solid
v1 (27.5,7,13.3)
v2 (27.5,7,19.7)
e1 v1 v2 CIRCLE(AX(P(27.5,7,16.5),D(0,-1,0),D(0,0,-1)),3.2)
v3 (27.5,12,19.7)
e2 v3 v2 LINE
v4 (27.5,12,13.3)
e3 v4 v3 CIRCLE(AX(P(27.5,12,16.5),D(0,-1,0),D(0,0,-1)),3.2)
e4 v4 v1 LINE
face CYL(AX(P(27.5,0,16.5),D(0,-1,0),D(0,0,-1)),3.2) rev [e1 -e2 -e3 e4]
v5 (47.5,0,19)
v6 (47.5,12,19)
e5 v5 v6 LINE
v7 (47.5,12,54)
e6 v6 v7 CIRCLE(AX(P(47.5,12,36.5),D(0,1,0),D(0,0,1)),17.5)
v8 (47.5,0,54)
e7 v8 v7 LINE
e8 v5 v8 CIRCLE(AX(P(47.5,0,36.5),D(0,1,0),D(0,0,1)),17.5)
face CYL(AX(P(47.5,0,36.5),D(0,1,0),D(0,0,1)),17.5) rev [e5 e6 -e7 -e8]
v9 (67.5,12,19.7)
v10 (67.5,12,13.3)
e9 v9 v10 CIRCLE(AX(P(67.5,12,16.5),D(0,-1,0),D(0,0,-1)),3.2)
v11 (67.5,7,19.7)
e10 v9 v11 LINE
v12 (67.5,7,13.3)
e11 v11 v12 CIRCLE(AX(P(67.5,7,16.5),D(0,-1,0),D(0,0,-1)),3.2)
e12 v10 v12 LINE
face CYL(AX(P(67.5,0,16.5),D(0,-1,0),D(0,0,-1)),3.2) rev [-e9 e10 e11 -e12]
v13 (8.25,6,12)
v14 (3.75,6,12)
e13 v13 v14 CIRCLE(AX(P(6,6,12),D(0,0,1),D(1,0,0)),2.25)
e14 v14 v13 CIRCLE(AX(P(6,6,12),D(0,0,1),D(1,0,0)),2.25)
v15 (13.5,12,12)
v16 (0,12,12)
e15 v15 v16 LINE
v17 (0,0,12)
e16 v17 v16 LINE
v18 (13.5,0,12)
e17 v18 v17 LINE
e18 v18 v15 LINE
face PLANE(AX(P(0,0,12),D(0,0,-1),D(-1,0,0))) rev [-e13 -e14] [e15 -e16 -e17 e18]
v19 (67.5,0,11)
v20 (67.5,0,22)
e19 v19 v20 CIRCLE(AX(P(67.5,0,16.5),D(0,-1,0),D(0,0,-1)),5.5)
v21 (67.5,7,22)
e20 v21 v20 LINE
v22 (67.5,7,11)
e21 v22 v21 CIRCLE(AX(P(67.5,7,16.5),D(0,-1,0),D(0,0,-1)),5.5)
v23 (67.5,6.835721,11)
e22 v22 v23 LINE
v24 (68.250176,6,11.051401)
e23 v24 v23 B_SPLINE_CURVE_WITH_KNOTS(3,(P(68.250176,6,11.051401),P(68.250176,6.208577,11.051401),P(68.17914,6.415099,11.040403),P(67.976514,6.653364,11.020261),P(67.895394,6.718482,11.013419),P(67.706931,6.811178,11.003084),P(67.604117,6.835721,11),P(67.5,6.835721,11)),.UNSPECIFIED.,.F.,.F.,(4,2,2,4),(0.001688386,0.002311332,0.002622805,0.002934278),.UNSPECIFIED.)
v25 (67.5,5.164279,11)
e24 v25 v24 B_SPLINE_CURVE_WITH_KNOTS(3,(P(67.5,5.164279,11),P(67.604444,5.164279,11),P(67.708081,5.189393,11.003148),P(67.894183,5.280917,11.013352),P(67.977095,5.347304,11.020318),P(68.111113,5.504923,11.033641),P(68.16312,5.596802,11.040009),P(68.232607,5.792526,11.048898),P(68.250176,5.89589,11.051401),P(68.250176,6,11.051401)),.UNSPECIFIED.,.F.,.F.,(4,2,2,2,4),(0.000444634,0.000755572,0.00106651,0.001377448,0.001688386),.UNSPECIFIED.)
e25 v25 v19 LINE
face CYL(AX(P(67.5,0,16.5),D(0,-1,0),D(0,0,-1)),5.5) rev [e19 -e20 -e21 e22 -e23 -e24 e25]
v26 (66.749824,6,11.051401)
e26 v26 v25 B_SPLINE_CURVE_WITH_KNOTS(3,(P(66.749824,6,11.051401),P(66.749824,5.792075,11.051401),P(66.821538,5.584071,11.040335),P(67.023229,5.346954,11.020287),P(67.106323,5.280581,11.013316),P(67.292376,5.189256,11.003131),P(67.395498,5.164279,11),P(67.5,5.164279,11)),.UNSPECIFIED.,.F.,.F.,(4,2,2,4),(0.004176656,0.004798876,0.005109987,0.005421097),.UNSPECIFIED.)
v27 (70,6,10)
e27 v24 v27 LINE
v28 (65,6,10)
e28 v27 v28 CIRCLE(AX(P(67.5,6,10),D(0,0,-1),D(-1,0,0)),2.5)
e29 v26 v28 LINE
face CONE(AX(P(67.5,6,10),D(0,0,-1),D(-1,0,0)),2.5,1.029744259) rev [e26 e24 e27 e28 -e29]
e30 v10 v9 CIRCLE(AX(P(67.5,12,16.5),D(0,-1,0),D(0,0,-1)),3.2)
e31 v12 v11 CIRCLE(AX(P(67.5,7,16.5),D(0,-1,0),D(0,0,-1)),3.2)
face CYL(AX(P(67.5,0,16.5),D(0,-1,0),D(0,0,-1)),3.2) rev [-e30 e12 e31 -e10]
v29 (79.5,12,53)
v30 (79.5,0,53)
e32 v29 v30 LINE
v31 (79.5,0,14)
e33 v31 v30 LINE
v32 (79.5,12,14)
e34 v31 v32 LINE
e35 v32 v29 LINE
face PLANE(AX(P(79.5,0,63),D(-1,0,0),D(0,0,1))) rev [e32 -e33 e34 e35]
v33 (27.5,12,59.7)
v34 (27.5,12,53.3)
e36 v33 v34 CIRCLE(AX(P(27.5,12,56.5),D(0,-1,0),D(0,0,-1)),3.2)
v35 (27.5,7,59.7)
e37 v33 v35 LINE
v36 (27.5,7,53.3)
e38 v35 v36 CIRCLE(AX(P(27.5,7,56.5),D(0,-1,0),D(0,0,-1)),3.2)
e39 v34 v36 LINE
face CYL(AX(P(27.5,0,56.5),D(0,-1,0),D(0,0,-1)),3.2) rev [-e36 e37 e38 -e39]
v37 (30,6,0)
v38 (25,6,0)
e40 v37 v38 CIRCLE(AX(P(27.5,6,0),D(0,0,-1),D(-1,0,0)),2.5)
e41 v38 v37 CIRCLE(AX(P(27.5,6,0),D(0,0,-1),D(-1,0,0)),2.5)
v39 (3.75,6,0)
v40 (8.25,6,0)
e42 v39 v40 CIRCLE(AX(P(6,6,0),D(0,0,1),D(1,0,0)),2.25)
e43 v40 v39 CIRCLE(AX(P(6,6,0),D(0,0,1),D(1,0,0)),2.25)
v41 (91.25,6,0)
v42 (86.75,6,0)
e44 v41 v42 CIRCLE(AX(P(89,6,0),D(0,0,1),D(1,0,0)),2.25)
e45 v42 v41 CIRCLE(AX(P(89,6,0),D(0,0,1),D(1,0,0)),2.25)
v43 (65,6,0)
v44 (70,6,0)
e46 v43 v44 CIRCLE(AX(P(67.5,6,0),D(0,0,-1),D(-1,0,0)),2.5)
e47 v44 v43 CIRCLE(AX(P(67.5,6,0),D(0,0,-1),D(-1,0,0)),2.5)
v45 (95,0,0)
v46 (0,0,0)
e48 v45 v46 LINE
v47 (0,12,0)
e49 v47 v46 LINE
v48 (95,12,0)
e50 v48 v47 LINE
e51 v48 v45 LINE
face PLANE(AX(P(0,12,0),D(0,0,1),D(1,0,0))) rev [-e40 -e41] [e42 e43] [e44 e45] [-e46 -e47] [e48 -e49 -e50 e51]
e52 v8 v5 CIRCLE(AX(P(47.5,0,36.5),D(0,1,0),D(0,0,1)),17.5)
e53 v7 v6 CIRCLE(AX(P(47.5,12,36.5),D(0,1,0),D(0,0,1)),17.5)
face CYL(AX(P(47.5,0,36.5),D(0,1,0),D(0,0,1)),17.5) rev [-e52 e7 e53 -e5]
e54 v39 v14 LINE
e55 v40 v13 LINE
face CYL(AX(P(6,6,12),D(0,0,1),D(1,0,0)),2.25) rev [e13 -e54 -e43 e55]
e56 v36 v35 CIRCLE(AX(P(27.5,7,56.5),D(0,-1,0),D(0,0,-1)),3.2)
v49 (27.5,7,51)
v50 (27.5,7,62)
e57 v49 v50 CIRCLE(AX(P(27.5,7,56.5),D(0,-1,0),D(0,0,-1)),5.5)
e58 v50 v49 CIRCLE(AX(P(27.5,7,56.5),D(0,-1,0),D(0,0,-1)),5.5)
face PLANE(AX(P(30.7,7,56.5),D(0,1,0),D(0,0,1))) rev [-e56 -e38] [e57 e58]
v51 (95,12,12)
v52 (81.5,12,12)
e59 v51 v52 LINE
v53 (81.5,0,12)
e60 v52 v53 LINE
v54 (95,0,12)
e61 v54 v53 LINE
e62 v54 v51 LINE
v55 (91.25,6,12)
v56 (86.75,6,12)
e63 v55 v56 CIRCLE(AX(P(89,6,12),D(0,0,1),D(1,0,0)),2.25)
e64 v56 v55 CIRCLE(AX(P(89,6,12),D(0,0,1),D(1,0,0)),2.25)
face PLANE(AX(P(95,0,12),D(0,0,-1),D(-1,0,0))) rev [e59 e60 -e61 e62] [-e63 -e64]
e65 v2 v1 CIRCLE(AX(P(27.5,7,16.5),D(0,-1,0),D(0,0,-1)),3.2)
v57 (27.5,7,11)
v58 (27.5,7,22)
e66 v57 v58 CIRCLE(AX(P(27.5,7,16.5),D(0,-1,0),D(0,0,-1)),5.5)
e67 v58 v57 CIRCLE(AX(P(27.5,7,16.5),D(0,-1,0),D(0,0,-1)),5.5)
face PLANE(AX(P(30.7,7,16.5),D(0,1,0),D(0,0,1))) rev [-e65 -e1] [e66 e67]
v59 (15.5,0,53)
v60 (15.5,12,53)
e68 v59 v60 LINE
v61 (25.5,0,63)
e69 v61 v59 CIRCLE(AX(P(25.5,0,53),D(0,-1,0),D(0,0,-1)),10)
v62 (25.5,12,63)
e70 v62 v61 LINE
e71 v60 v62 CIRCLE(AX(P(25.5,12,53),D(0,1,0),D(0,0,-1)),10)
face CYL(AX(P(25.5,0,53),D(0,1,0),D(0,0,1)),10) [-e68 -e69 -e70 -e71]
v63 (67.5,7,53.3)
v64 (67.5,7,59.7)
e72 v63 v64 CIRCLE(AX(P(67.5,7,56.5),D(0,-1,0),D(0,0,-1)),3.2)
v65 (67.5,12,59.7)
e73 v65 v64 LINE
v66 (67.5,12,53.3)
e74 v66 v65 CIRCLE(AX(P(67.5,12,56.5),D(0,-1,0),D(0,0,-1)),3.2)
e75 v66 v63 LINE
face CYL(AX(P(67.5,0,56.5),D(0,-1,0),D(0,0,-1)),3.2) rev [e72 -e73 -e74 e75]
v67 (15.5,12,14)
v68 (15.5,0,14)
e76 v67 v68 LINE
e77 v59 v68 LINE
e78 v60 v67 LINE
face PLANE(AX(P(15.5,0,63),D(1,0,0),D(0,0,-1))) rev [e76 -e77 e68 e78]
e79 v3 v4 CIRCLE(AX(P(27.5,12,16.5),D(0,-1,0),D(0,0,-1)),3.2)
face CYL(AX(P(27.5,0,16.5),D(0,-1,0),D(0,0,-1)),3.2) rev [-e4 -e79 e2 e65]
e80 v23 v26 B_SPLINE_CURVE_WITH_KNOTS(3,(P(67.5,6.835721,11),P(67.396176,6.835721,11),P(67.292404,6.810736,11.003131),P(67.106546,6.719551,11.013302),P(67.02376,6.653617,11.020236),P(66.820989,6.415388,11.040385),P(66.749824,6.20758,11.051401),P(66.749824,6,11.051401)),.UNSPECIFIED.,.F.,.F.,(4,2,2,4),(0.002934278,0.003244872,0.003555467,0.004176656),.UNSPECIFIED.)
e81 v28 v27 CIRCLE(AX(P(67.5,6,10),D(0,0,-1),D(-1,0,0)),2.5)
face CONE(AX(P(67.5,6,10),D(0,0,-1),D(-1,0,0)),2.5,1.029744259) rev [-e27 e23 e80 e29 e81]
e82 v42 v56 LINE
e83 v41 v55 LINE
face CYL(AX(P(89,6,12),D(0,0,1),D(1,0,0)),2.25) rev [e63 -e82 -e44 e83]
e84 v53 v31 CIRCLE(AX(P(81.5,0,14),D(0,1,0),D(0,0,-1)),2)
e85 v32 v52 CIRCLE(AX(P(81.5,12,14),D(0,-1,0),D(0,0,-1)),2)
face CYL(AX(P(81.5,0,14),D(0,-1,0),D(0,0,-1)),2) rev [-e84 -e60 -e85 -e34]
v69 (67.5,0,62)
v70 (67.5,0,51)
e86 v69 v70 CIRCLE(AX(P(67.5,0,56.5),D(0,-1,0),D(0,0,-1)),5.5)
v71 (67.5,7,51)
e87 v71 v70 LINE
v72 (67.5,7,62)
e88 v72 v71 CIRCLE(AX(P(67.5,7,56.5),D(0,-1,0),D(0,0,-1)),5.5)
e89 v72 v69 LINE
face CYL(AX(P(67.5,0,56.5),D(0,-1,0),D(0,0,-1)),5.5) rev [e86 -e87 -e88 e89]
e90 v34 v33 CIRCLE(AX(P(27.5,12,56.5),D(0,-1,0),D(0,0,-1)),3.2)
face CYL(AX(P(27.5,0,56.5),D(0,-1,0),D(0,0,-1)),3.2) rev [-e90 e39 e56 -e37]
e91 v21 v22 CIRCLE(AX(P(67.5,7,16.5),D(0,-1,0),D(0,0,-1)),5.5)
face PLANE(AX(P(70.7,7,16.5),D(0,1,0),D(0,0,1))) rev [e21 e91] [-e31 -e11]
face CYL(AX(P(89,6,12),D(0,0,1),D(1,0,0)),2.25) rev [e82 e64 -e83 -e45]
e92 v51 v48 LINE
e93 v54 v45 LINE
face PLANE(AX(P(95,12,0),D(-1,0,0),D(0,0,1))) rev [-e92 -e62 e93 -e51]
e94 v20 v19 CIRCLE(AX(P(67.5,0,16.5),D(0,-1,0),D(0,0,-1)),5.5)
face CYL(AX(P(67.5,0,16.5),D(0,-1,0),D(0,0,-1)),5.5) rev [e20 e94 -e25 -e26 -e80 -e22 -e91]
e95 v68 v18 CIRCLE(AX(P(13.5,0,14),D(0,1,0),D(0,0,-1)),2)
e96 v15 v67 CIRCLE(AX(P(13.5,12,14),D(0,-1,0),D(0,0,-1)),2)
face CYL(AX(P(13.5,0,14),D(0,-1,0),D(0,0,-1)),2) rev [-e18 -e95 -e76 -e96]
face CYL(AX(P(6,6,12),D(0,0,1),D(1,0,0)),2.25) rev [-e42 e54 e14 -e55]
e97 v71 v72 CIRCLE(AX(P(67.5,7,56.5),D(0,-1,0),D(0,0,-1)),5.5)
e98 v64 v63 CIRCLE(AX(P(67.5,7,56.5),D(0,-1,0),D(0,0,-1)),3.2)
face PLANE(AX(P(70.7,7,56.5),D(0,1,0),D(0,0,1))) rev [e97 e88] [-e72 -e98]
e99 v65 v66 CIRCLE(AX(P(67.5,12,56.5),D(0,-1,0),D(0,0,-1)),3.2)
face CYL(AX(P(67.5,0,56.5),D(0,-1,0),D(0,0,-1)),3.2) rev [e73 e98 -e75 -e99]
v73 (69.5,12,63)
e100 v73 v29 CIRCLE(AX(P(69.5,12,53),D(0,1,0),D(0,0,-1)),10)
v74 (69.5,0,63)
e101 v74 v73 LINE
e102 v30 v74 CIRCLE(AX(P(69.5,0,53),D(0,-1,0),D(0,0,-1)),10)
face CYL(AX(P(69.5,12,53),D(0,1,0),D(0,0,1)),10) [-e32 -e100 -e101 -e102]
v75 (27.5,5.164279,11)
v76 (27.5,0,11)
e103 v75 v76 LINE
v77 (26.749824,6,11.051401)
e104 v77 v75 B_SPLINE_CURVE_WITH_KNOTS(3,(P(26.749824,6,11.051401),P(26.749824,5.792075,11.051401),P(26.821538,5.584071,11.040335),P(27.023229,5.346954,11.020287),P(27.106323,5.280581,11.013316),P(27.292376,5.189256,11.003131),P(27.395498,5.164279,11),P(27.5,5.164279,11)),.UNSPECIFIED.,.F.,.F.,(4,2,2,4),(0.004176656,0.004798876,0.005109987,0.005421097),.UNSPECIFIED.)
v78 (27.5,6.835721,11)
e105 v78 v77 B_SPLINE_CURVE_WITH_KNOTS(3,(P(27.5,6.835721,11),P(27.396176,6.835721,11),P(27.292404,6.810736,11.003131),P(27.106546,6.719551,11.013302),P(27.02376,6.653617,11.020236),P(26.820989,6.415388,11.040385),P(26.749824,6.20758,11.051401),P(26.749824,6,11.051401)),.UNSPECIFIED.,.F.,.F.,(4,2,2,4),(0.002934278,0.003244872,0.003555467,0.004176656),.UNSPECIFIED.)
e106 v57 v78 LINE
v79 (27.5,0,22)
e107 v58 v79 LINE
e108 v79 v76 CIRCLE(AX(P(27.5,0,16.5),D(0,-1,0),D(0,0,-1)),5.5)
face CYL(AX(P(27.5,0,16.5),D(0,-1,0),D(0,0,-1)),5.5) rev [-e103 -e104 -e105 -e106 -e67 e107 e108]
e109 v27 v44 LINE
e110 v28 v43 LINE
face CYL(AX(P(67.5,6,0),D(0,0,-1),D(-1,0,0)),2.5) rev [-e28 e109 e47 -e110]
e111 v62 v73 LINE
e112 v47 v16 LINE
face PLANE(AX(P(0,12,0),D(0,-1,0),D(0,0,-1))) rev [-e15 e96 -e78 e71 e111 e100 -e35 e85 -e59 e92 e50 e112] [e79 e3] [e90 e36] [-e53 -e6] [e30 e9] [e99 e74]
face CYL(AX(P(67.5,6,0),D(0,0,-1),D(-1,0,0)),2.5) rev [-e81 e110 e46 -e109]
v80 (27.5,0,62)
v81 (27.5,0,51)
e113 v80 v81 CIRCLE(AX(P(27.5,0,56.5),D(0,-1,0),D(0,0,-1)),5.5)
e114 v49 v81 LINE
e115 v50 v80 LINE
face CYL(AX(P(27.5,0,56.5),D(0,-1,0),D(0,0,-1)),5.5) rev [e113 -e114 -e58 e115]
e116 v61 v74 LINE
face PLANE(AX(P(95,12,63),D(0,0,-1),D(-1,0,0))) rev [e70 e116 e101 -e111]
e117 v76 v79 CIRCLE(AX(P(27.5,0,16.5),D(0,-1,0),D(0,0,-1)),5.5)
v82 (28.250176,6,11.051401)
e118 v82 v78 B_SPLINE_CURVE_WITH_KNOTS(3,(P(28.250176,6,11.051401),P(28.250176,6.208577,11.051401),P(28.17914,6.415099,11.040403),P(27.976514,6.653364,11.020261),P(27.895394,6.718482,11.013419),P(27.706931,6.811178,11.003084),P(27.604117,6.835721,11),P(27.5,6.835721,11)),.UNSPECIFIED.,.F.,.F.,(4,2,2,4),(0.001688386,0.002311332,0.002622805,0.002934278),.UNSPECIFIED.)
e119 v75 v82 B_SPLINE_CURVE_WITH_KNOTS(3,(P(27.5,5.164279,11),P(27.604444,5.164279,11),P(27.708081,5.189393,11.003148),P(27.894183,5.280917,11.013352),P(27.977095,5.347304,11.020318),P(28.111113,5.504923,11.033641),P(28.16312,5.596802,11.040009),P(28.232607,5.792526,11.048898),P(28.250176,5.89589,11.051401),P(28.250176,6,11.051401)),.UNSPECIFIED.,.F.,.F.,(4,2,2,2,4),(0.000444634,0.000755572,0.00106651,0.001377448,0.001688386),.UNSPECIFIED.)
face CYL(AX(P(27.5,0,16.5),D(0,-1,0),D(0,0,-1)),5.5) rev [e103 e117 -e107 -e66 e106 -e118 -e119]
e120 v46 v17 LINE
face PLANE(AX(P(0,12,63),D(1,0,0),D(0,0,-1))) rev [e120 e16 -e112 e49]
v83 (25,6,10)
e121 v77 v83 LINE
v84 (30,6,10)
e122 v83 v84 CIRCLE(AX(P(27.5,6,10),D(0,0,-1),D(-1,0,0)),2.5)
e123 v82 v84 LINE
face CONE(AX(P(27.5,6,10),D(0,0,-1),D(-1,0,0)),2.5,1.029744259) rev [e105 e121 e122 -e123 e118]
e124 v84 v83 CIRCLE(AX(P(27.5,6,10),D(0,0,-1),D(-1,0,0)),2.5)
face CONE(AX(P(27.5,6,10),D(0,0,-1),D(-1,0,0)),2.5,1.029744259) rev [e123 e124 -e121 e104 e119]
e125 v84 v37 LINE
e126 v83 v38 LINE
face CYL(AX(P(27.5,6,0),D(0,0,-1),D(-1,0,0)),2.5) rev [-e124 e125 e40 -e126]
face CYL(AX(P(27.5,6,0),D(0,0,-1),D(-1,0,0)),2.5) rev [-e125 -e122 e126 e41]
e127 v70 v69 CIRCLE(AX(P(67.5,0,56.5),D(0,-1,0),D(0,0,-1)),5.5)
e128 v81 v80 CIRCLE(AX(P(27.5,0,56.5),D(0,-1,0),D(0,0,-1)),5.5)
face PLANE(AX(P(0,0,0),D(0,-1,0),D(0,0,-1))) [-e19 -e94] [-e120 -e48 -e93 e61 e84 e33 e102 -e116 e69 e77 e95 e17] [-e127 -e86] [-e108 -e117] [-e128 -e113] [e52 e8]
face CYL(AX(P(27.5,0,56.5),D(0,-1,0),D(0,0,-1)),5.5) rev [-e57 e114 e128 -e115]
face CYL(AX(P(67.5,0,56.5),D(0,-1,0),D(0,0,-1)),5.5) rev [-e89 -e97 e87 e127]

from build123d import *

# Parameters (mm, degrees)
SKETCH_1_W                = 95
SKETCH_1_H                = 63
EXTRUDE_1_DEPTH           = 12
SKETCH_9_W                = 15.5
SKETCH_9_H                = 51
CUT_EXTRUDE_4_DEPTH       = 115.621114983
HOLE_WIZARD_6_5_6_5_1_D   = 4.5
SKETCH_12_R               = 17.5
CUT_EXTRUDE_5_DEPTH       = 115.621114983
FILLET_1_R                = 10
HOLE_WIZARD_5_0_5_1_D     = 5
HOLE_WIZARD_5_0_5_1_DEPTH = 10
HOLE_WIZARD_5_0_5_1_TIP   = 1.502151548
FILLET_2_R                = 2
HOLE_WIZARD_1_D           = 6.4
HOLE_WIZARD_1_CBORE_D     = 11
HOLE_WIZARD_1_CBORE_DEPTH = 7


with BuildPart() as part:
    # 草图1 → 凸台-拉伸1 (new body)
    with BuildSketch(Plane(origin=(0, 0, 0), x_dir=(1, 0, 0), z_dir=(0, 1, 0))):
        with Locations((47.5, -31.5)):
            Rectangle(SKETCH_1_W, SKETCH_1_H)
    extrude(amount=EXTRUDE_1_DEPTH)

    # 草图9 → 切除-拉伸4 (cut, through all)
    with BuildSketch(Plane(origin=(0, 12, 0), x_dir=(1, 0, 0), z_dir=(0, 1, 0))):
        with Locations((7.75, -37.5)):
            Rectangle(SKETCH_9_W, SKETCH_9_H)
        with Locations((87.25, -37.5)):
            Rectangle(SKETCH_9_W, SKETCH_9_H)
    extrude(amount=-CUT_EXTRUDE_4_DEPTH, mode=Mode.SUBTRACT)

    # Ø6.5 (6.5) 直径孔1 (through all)
    with Locations(Plane.XY.offset(12)):
        with Locations((6, 6), (89, 6)):
            Hole(HOLE_WIZARD_6_5_6_5_1_D / 2)

    # 草图12 → 切除-拉伸5 (cut, through all)
    with BuildSketch(Plane(origin=(0, 12, 0), x_dir=(1, 0, 0), z_dir=(0, 1, 0))):
        with Locations(Location((47.5, -36.5, 0), (0, 0, 270))):
            Circle(SKETCH_12_R)
    extrude(amount=-CUT_EXTRUDE_5_DEPTH, mode=Mode.SUBTRACT)

    # 圆角1
    fillet_1_edges = [part.edges().sort_by_distance(p)[0] for p in [
        (15.5, 6, 63),
        (79.5, 6, 63),
    ]]
    fillet(fillet_1_edges, radius=FILLET_1_R)

    # Ø5.0 (5) 直径孔1
    with Locations(Plane(origin=(0, 0, 0), x_dir=(-1, 0, 0), z_dir=(0, 0, -1))):
        with Locations((-67.5, 6), (-27.5, 6)):
            Hole(HOLE_WIZARD_5_0_5_1_D / 2, depth=HOLE_WIZARD_5_0_5_1_DEPTH)
            with Locations((0, 0, -(HOLE_WIZARD_5_0_5_1_DEPTH + HOLE_WIZARD_5_0_5_1_TIP / 2))):  # 118° drill point
                Cone(0, HOLE_WIZARD_5_0_5_1_D / 2, HOLE_WIZARD_5_0_5_1_TIP, mode=Mode.SUBTRACT)

    # 圆角2
    fillet_2_edges = [part.edges().sort_by_distance(p)[0] for p in [
        (15.5, 6, 12),
        (79.5, 6, 12),
    ]]
    fillet(fillet_2_edges, radius=FILLET_2_R)

    # 打孔尺寸(%根据)内六角圆柱头螺钉的类型1 (through all)
    with Locations(Plane(origin=(0, 0, 0), x_dir=(-1, 0, 0), z_dir=(0, -1, 0))):
        with Locations((-67.5, -56.5), (-27.5, -56.5), (-27.5, -16.5), (-67.5, -16.5)):
            CounterBoreHole(HOLE_WIZARD_1_D / 2, HOLE_WIZARD_1_CBORE_D / 2, HOLE_WIZARD_1_CBORE_DEPTH)


solid = part.part
